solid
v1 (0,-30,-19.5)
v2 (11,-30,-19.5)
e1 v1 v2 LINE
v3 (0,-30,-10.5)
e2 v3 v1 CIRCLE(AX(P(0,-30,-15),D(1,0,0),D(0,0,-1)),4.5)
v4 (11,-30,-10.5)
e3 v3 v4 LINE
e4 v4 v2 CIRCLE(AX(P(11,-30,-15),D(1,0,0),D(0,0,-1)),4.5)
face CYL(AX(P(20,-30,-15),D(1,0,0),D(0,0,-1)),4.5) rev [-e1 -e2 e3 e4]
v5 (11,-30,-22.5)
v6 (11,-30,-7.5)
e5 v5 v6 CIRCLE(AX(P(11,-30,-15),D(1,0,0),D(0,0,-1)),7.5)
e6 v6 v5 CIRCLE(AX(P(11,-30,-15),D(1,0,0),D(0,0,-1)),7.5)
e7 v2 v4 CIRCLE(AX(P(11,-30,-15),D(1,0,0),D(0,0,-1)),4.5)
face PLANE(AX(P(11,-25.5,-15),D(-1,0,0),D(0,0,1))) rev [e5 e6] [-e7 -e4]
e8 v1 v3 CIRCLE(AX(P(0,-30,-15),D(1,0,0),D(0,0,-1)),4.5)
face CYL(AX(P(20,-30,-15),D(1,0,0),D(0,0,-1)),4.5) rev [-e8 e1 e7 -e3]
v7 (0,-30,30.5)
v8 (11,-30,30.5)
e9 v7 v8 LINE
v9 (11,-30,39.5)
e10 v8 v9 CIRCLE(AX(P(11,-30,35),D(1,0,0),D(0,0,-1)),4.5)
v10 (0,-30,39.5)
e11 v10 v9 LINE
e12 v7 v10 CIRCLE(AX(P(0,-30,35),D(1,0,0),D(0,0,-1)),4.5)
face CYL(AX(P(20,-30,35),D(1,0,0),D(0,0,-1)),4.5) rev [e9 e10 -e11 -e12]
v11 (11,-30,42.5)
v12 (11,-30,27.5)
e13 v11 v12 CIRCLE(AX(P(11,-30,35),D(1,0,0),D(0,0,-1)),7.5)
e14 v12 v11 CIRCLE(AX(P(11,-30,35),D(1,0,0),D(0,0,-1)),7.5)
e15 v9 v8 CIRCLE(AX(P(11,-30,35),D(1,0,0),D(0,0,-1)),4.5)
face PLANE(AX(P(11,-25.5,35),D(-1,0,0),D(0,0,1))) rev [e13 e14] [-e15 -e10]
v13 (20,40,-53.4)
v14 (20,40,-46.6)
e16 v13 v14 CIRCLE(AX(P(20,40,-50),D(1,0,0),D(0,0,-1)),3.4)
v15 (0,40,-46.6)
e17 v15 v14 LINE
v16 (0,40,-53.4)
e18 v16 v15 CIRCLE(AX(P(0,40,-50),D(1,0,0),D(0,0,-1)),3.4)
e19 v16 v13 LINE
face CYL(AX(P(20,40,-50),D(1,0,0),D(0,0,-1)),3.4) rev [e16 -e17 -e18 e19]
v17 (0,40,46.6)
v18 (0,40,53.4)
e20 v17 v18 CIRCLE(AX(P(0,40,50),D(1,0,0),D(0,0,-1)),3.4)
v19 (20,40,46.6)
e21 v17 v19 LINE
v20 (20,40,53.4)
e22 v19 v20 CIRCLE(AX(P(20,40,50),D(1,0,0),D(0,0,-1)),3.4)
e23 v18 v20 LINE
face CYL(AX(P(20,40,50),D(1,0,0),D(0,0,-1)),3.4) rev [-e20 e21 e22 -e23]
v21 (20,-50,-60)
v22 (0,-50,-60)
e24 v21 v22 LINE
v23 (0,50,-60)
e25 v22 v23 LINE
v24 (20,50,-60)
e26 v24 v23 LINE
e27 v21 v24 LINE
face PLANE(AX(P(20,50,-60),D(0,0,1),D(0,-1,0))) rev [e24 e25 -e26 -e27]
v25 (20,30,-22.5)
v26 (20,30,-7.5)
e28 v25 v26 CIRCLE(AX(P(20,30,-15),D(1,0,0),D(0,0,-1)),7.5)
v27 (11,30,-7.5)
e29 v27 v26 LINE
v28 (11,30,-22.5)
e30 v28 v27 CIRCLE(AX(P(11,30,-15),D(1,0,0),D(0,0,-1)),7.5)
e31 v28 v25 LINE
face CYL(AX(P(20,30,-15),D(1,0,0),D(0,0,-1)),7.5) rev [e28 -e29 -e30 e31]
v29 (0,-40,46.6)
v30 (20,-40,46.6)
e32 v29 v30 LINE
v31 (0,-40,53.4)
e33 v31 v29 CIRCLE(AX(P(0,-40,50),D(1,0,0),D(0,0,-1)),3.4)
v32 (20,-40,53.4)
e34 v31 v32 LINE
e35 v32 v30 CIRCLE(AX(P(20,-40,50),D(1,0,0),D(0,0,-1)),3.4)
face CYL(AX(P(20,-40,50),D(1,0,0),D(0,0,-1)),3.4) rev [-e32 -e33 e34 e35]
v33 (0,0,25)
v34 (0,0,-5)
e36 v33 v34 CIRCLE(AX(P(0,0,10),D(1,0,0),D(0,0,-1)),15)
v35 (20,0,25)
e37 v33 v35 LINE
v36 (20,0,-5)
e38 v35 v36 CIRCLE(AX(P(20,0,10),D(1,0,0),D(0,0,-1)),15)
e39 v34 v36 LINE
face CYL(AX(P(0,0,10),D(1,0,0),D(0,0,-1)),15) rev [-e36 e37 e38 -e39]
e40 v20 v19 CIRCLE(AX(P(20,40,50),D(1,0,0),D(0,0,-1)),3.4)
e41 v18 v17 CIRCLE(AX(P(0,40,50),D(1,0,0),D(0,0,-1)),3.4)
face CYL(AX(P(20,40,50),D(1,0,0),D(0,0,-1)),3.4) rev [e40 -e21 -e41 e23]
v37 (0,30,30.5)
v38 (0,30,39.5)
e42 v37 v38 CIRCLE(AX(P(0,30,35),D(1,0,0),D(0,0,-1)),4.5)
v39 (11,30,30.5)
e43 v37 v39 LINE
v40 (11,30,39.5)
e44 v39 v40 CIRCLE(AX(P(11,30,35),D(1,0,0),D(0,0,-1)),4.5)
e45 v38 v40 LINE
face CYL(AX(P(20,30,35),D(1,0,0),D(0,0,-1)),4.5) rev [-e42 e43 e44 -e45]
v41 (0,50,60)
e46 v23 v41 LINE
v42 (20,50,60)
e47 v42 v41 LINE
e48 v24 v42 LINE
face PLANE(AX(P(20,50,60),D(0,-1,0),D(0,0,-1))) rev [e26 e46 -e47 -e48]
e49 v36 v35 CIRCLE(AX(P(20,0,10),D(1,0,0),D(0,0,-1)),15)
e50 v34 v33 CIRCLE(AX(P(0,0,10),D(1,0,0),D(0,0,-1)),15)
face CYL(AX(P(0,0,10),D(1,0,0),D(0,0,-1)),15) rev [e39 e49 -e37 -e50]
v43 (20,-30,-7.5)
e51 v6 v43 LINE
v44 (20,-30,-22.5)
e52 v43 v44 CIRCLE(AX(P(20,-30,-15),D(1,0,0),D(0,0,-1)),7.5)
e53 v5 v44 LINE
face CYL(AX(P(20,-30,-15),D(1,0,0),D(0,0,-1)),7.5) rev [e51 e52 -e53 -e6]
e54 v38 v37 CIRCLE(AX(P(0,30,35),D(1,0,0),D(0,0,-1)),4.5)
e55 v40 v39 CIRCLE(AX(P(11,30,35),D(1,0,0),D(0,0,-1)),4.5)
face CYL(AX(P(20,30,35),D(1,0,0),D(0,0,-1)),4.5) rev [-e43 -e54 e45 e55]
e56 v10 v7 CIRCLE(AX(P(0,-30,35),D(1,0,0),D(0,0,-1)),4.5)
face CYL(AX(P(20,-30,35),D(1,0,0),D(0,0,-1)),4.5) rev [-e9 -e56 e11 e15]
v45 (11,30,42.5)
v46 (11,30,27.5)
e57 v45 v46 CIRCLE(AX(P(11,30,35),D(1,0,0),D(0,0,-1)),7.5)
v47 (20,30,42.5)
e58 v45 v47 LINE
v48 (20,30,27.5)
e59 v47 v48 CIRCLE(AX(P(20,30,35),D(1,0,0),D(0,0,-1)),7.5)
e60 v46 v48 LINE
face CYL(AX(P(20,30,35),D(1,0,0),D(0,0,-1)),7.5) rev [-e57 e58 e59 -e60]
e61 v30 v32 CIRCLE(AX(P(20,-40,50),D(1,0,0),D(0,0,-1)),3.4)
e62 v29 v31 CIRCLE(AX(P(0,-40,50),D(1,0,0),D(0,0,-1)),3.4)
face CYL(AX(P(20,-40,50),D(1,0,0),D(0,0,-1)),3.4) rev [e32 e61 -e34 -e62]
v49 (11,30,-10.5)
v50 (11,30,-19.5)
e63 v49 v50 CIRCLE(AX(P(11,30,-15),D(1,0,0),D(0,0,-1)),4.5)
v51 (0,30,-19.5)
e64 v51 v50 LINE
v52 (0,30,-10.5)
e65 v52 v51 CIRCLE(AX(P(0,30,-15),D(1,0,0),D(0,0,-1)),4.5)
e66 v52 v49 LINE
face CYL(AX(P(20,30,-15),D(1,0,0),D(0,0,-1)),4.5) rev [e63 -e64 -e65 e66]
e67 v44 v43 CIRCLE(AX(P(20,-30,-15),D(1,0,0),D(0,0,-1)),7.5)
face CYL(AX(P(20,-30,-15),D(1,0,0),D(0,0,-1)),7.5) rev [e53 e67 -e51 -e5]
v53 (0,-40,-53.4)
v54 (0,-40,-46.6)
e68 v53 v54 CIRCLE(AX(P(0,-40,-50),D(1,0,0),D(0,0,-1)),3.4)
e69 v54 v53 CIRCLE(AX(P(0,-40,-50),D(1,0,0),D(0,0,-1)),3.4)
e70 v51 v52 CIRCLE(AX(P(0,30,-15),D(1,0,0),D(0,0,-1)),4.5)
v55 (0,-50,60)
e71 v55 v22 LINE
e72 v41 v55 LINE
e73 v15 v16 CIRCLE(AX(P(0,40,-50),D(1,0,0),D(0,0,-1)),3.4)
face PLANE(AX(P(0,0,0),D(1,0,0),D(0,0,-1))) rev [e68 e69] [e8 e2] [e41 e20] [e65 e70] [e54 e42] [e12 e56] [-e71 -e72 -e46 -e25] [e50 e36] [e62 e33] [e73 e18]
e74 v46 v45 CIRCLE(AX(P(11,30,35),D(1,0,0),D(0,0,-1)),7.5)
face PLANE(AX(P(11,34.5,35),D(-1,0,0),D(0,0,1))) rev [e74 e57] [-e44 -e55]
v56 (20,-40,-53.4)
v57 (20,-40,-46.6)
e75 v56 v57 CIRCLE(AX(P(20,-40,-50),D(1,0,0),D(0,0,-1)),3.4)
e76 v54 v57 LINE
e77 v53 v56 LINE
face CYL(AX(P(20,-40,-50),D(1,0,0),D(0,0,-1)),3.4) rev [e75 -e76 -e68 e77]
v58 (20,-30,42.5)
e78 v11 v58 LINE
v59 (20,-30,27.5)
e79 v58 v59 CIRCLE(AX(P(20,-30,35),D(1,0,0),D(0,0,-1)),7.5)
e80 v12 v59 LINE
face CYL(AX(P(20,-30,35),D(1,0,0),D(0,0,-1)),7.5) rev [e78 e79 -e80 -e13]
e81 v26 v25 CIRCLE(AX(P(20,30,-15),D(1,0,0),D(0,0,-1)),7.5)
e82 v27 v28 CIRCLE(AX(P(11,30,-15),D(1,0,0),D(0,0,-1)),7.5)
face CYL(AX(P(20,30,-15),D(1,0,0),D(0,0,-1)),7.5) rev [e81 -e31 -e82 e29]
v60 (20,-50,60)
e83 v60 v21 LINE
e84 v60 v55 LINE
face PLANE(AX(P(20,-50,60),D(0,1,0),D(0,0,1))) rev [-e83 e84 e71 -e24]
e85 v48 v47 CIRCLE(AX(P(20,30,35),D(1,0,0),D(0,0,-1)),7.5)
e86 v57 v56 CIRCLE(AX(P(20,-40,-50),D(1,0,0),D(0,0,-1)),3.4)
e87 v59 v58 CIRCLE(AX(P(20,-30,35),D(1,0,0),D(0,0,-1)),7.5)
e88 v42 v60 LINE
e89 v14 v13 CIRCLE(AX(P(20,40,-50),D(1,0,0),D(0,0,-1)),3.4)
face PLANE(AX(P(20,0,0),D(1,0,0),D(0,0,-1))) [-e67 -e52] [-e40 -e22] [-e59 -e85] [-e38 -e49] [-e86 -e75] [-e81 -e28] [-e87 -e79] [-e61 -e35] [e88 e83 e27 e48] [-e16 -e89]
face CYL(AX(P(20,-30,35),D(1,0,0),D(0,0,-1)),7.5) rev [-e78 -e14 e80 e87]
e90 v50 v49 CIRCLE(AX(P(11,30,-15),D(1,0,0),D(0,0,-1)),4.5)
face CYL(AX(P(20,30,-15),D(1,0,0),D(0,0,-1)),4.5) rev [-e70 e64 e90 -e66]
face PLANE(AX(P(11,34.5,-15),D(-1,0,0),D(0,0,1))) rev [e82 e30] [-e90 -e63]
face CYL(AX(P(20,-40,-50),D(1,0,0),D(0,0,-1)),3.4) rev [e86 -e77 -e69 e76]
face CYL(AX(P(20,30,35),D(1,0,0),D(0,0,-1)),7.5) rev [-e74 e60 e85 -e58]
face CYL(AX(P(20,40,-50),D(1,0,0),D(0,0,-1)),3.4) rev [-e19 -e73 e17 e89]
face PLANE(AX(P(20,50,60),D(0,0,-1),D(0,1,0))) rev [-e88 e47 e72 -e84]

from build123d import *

# Parameters (mm, degrees)
SKETCH_1_W                = 120
SKETCH_1_H                = 100
EXTRUDE_1_DEPTH           = 20
HOLE_WIZARD_1_D           = 9
HOLE_WIZARD_1_CBORE_D     = 15
HOLE_WIZARD_1_CBORE_DEPTH = 9
SKETCH_4_R                = 15
CUT_EXTRUDE_1_DEPTH       = 81.622577483
HOLE_WIZARD_M8_1_D        = 6.8


with BuildPart() as part:
    # 草图1 → 凸台-拉伸1 (new body)
    with BuildSketch(Plane(origin=(0, 0, 0), x_dir=(0, 0, -1), z_dir=(1, 0, 0))):
        Rectangle(SKETCH_1_W, SKETCH_1_H)
    extrude(amount=EXTRUDE_1_DEPTH)

    # 打孔尺寸(%根据)内六角圆柱头螺钉的类型1 (through all)
    with Locations(Plane(origin=(20, 0, 0), x_dir=(0, 0, -1), z_dir=(1, 0, 0))):
        with Locations((-35, 30), (15, 30), (-35, -30), (15, -30)):
            CounterBoreHole(HOLE_WIZARD_1_D / 2, HOLE_WIZARD_1_CBORE_D / 2, HOLE_WIZARD_1_CBORE_DEPTH)

    # 草图4 → 切除-拉伸1 (cut, through all)
    with BuildSketch(Plane(origin=(20, 0, 0), x_dir=(0, 0, -1), z_dir=(1, 0, 0))):
        with Locations((-10, 0)):
            Circle(SKETCH_4_R)
    extrude(amount=-CUT_EXTRUDE_1_DEPTH, mode=Mode.SUBTRACT)

    # M8 螺纹孔1 (through all)
    with Locations(Plane(origin=(20, 0, 0), x_dir=(0, 0, -1), z_dir=(1, 0, 0))):
        with Locations((-50, 40), (-50, -40), (50, -40), (50, 40)):
            Hole(HOLE_WIZARD_M8_1_D / 2)


solid = part.part
